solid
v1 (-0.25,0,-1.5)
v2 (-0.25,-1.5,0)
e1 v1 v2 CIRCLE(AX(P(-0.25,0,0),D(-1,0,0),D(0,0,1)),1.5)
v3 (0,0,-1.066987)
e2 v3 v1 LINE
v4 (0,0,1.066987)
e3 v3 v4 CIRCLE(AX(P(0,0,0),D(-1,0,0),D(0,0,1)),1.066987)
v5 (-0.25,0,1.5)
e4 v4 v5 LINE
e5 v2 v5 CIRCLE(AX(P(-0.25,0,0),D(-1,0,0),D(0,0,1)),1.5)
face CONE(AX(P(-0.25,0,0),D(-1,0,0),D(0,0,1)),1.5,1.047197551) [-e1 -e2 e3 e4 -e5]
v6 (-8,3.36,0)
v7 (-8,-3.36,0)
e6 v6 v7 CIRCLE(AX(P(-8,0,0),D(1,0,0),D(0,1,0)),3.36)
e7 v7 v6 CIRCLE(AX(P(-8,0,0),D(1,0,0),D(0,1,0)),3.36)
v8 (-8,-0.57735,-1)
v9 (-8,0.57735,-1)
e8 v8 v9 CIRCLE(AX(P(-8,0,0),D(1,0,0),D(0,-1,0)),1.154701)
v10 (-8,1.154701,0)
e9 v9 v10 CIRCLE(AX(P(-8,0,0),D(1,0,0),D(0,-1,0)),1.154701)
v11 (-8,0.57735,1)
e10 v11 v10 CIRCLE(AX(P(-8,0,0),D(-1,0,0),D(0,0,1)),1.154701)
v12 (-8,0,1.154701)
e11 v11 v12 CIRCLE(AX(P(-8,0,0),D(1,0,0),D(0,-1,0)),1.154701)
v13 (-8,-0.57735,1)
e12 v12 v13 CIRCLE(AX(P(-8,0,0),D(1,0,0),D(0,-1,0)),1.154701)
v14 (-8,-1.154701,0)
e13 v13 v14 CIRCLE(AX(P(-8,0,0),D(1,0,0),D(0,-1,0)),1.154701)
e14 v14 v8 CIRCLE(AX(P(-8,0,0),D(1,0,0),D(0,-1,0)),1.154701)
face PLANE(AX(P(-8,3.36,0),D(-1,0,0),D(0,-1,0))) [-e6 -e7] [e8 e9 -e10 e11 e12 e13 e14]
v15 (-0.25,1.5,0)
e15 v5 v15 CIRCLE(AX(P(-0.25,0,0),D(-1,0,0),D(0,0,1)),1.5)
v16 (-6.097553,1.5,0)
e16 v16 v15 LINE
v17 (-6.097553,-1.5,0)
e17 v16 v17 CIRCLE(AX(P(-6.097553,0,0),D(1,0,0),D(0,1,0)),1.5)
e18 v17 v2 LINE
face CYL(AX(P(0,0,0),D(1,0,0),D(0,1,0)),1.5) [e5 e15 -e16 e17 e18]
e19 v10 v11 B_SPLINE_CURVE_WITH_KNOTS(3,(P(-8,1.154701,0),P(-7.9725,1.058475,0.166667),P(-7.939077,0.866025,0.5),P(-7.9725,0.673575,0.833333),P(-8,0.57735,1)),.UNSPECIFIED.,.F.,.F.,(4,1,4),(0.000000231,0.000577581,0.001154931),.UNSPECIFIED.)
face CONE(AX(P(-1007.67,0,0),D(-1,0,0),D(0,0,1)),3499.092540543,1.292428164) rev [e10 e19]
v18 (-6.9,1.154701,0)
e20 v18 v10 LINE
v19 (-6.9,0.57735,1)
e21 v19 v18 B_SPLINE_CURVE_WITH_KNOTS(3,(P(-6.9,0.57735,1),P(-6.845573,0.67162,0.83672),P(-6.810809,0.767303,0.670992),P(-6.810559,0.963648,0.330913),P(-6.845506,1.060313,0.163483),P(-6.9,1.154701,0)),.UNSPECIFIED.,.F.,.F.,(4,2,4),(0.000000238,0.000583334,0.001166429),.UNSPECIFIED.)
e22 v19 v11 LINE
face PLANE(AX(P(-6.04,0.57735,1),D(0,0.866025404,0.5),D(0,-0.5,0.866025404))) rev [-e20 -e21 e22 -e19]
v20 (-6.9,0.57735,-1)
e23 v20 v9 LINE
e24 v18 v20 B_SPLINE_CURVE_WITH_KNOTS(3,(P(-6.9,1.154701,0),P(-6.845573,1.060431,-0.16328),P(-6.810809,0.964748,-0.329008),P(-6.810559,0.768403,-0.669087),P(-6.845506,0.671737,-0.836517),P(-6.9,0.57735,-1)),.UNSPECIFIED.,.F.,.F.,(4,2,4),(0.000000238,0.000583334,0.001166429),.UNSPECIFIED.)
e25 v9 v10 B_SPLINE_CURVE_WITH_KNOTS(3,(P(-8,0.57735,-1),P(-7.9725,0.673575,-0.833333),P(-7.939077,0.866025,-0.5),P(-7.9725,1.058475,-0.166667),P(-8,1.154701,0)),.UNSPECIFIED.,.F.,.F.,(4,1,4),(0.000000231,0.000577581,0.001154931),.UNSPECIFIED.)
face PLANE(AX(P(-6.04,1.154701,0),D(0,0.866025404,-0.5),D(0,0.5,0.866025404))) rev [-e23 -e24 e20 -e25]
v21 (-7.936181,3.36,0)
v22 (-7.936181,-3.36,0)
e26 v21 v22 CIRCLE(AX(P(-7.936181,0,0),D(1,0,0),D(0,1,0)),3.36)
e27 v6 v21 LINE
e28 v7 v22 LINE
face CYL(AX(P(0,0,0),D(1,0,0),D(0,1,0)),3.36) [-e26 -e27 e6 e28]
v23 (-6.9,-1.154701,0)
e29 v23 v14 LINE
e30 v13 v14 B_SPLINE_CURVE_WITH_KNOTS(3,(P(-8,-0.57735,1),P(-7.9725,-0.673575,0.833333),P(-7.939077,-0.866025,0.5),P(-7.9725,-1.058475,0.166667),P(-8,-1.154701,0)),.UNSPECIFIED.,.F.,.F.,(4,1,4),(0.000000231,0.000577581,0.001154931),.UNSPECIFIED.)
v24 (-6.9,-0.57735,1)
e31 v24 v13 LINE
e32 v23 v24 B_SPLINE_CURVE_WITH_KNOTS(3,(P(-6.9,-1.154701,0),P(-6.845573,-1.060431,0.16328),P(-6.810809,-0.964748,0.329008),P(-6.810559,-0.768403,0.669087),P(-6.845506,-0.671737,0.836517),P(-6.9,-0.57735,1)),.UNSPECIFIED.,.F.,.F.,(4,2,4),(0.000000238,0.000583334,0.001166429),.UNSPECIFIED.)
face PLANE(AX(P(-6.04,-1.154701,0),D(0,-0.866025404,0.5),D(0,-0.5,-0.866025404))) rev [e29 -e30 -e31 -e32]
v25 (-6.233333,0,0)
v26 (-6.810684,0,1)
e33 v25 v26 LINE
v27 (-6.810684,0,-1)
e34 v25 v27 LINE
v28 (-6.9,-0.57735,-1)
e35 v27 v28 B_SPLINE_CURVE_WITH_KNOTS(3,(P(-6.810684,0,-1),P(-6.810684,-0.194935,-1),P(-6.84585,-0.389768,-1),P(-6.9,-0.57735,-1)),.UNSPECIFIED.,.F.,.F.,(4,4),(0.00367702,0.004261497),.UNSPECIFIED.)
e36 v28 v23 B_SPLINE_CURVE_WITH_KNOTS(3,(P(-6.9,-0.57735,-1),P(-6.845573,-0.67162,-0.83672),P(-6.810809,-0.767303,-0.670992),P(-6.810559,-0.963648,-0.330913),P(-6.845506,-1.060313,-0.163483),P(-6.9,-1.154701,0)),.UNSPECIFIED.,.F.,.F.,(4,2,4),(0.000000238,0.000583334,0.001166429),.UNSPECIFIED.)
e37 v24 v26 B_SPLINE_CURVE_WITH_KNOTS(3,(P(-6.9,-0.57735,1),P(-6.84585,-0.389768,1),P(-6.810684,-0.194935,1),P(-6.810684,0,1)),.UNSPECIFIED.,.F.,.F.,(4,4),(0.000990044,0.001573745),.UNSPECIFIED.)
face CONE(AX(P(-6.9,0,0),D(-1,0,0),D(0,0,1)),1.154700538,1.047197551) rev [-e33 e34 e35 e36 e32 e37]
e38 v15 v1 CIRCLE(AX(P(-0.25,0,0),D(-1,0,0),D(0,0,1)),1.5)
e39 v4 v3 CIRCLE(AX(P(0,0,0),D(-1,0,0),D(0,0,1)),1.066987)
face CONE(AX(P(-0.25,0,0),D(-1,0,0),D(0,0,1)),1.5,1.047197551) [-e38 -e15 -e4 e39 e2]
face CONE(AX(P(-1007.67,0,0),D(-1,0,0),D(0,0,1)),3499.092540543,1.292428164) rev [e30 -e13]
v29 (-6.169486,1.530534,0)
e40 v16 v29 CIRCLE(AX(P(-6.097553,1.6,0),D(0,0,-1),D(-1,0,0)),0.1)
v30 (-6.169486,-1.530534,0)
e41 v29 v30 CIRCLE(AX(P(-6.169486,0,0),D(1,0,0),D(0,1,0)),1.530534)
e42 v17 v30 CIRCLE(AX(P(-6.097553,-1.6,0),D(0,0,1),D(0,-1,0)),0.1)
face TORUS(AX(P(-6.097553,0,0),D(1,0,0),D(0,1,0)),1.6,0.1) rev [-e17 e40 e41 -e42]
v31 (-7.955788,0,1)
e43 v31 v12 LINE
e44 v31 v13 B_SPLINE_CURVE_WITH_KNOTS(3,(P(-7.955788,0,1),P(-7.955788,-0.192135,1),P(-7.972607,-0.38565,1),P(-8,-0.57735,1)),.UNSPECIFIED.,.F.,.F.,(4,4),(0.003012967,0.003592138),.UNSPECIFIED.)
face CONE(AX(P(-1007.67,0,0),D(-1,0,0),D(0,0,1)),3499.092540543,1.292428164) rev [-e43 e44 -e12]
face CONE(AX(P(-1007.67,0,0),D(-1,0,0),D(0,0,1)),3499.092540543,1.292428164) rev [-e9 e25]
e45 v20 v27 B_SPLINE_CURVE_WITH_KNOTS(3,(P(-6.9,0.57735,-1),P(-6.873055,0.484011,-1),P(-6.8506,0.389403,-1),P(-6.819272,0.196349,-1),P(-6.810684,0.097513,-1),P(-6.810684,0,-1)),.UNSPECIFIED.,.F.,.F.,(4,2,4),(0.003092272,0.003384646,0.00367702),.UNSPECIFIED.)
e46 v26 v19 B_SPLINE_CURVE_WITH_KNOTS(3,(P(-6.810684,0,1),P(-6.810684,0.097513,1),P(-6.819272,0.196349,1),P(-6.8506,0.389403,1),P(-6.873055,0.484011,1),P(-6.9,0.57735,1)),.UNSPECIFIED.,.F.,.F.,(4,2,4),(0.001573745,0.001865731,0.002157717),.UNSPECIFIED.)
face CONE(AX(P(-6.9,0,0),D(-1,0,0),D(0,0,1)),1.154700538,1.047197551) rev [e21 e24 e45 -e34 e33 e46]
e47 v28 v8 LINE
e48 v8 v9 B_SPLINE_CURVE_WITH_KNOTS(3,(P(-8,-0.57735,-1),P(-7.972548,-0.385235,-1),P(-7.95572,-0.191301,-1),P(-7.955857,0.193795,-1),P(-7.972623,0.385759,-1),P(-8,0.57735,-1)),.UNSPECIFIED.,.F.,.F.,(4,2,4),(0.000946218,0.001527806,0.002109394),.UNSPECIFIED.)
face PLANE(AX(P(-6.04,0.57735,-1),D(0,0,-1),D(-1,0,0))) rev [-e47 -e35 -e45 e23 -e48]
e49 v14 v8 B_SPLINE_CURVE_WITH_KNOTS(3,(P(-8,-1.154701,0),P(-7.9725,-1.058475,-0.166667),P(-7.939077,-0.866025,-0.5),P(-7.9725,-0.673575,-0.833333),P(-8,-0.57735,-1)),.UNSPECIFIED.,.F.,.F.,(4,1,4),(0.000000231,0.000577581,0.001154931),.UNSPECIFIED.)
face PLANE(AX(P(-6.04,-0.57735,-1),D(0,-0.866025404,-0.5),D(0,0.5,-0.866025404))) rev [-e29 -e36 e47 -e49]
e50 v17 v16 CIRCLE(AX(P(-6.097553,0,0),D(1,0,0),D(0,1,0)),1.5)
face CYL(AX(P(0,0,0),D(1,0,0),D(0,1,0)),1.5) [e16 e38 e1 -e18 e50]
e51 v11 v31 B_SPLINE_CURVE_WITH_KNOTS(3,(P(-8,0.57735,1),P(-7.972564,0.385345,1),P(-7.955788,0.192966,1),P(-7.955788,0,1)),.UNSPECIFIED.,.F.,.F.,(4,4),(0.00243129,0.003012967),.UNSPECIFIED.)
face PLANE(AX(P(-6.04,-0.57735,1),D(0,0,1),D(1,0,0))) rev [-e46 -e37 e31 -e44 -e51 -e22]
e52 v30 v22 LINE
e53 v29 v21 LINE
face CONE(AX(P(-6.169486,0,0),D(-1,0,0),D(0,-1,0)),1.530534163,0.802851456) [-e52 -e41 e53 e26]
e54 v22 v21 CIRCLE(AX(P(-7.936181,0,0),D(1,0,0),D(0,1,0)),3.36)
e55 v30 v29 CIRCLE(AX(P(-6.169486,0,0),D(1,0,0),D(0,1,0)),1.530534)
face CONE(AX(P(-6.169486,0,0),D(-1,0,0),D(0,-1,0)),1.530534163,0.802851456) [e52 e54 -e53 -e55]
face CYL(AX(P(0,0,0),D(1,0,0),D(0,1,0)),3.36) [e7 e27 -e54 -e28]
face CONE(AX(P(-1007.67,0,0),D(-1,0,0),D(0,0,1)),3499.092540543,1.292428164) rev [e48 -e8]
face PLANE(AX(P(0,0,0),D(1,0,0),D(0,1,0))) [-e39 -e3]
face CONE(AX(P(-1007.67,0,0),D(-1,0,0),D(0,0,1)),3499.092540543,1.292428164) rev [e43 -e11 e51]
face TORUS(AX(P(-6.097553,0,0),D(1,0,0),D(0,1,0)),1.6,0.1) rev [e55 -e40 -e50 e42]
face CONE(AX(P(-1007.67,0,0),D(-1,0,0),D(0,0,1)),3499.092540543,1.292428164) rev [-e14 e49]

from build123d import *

# Parameters (mm, degrees)
CUT_EXTRUDE1_DEPTH = 1.96


with BuildPart() as part:
    # Sketch1 → Revolve1 (revolve)
    with BuildSketch(Plane.XY):
        with BuildLine():
            Line((0, 1.5), (-6.097552518, 1.5))
            ThreePointArc((-6.097552518, 1.5), (-6.136625631, 1.507949515), (-6.169486498, 1.530534163))
            Line((-6.169486498, 1.530534163), (-7.936181121, 3.36))
            Line((-7.936181121, 3.36), (-8, 3.36))
            Line((-8, 3.36), (-8, 0))
            Line((-8, 0), (0, 0))
            Line((0, 0), (0, 1.5))
        make_face()
    revolve(axis=Axis((0, 0, 0), (-1, 0, 0)))

    # Sketch2 → Cut-Extrude1 (cut)
    with BuildSketch(Plane.ZY.offset(8)):
        Polygon((0, 1.154700538), (-1, 0.577350269), (-1, -0.577350269), (0, -1.154700538), (1, -0.577350269), (1, 0.577350269), align=None)
    extrude(amount=-CUT_EXTRUDE1_DEPTH, mode=Mode.SUBTRACT)

    # Sketch6 → Revolve2 (revolve)
    with BuildSketch(Plane.XY, mode=Mode.PRIVATE) as revolve2_sk:
        Polygon((-6.9, 1.154700538), (-6.233333333, 0), (-5.74, 0), (-5.74, 1.154700538), align=None)
    revolve(revolve2_sk.sketch.rotate(Axis((-8, 0, 0), (1, 0, 0)), 90), axis=Axis((-8, 0, 0), (1, 0, 0)))

    # Sketch7 → Cut-Revolve2 (revolve, cut)
    with BuildSketch(Plane.XY):
        Polygon((-8, 1.154700538), (-8, 0), (-7.67, 0), align=None)
    revolve(axis=Axis((-8, 0, 0), (1, 0, 0)), mode=Mode.SUBTRACT)

    # Sketch4 → Cut-Revolve1 (revolve, cut)
    with BuildSketch(Plane.XY):
        Polygon((-0.25, 1.5), (0, 1.066987298), (0.25, 1.5), align=None)
    revolve(axis=Axis((-0.25, 0, 0), (1, 0, 0)), mode=Mode.SUBTRACT)


solid = part.part
